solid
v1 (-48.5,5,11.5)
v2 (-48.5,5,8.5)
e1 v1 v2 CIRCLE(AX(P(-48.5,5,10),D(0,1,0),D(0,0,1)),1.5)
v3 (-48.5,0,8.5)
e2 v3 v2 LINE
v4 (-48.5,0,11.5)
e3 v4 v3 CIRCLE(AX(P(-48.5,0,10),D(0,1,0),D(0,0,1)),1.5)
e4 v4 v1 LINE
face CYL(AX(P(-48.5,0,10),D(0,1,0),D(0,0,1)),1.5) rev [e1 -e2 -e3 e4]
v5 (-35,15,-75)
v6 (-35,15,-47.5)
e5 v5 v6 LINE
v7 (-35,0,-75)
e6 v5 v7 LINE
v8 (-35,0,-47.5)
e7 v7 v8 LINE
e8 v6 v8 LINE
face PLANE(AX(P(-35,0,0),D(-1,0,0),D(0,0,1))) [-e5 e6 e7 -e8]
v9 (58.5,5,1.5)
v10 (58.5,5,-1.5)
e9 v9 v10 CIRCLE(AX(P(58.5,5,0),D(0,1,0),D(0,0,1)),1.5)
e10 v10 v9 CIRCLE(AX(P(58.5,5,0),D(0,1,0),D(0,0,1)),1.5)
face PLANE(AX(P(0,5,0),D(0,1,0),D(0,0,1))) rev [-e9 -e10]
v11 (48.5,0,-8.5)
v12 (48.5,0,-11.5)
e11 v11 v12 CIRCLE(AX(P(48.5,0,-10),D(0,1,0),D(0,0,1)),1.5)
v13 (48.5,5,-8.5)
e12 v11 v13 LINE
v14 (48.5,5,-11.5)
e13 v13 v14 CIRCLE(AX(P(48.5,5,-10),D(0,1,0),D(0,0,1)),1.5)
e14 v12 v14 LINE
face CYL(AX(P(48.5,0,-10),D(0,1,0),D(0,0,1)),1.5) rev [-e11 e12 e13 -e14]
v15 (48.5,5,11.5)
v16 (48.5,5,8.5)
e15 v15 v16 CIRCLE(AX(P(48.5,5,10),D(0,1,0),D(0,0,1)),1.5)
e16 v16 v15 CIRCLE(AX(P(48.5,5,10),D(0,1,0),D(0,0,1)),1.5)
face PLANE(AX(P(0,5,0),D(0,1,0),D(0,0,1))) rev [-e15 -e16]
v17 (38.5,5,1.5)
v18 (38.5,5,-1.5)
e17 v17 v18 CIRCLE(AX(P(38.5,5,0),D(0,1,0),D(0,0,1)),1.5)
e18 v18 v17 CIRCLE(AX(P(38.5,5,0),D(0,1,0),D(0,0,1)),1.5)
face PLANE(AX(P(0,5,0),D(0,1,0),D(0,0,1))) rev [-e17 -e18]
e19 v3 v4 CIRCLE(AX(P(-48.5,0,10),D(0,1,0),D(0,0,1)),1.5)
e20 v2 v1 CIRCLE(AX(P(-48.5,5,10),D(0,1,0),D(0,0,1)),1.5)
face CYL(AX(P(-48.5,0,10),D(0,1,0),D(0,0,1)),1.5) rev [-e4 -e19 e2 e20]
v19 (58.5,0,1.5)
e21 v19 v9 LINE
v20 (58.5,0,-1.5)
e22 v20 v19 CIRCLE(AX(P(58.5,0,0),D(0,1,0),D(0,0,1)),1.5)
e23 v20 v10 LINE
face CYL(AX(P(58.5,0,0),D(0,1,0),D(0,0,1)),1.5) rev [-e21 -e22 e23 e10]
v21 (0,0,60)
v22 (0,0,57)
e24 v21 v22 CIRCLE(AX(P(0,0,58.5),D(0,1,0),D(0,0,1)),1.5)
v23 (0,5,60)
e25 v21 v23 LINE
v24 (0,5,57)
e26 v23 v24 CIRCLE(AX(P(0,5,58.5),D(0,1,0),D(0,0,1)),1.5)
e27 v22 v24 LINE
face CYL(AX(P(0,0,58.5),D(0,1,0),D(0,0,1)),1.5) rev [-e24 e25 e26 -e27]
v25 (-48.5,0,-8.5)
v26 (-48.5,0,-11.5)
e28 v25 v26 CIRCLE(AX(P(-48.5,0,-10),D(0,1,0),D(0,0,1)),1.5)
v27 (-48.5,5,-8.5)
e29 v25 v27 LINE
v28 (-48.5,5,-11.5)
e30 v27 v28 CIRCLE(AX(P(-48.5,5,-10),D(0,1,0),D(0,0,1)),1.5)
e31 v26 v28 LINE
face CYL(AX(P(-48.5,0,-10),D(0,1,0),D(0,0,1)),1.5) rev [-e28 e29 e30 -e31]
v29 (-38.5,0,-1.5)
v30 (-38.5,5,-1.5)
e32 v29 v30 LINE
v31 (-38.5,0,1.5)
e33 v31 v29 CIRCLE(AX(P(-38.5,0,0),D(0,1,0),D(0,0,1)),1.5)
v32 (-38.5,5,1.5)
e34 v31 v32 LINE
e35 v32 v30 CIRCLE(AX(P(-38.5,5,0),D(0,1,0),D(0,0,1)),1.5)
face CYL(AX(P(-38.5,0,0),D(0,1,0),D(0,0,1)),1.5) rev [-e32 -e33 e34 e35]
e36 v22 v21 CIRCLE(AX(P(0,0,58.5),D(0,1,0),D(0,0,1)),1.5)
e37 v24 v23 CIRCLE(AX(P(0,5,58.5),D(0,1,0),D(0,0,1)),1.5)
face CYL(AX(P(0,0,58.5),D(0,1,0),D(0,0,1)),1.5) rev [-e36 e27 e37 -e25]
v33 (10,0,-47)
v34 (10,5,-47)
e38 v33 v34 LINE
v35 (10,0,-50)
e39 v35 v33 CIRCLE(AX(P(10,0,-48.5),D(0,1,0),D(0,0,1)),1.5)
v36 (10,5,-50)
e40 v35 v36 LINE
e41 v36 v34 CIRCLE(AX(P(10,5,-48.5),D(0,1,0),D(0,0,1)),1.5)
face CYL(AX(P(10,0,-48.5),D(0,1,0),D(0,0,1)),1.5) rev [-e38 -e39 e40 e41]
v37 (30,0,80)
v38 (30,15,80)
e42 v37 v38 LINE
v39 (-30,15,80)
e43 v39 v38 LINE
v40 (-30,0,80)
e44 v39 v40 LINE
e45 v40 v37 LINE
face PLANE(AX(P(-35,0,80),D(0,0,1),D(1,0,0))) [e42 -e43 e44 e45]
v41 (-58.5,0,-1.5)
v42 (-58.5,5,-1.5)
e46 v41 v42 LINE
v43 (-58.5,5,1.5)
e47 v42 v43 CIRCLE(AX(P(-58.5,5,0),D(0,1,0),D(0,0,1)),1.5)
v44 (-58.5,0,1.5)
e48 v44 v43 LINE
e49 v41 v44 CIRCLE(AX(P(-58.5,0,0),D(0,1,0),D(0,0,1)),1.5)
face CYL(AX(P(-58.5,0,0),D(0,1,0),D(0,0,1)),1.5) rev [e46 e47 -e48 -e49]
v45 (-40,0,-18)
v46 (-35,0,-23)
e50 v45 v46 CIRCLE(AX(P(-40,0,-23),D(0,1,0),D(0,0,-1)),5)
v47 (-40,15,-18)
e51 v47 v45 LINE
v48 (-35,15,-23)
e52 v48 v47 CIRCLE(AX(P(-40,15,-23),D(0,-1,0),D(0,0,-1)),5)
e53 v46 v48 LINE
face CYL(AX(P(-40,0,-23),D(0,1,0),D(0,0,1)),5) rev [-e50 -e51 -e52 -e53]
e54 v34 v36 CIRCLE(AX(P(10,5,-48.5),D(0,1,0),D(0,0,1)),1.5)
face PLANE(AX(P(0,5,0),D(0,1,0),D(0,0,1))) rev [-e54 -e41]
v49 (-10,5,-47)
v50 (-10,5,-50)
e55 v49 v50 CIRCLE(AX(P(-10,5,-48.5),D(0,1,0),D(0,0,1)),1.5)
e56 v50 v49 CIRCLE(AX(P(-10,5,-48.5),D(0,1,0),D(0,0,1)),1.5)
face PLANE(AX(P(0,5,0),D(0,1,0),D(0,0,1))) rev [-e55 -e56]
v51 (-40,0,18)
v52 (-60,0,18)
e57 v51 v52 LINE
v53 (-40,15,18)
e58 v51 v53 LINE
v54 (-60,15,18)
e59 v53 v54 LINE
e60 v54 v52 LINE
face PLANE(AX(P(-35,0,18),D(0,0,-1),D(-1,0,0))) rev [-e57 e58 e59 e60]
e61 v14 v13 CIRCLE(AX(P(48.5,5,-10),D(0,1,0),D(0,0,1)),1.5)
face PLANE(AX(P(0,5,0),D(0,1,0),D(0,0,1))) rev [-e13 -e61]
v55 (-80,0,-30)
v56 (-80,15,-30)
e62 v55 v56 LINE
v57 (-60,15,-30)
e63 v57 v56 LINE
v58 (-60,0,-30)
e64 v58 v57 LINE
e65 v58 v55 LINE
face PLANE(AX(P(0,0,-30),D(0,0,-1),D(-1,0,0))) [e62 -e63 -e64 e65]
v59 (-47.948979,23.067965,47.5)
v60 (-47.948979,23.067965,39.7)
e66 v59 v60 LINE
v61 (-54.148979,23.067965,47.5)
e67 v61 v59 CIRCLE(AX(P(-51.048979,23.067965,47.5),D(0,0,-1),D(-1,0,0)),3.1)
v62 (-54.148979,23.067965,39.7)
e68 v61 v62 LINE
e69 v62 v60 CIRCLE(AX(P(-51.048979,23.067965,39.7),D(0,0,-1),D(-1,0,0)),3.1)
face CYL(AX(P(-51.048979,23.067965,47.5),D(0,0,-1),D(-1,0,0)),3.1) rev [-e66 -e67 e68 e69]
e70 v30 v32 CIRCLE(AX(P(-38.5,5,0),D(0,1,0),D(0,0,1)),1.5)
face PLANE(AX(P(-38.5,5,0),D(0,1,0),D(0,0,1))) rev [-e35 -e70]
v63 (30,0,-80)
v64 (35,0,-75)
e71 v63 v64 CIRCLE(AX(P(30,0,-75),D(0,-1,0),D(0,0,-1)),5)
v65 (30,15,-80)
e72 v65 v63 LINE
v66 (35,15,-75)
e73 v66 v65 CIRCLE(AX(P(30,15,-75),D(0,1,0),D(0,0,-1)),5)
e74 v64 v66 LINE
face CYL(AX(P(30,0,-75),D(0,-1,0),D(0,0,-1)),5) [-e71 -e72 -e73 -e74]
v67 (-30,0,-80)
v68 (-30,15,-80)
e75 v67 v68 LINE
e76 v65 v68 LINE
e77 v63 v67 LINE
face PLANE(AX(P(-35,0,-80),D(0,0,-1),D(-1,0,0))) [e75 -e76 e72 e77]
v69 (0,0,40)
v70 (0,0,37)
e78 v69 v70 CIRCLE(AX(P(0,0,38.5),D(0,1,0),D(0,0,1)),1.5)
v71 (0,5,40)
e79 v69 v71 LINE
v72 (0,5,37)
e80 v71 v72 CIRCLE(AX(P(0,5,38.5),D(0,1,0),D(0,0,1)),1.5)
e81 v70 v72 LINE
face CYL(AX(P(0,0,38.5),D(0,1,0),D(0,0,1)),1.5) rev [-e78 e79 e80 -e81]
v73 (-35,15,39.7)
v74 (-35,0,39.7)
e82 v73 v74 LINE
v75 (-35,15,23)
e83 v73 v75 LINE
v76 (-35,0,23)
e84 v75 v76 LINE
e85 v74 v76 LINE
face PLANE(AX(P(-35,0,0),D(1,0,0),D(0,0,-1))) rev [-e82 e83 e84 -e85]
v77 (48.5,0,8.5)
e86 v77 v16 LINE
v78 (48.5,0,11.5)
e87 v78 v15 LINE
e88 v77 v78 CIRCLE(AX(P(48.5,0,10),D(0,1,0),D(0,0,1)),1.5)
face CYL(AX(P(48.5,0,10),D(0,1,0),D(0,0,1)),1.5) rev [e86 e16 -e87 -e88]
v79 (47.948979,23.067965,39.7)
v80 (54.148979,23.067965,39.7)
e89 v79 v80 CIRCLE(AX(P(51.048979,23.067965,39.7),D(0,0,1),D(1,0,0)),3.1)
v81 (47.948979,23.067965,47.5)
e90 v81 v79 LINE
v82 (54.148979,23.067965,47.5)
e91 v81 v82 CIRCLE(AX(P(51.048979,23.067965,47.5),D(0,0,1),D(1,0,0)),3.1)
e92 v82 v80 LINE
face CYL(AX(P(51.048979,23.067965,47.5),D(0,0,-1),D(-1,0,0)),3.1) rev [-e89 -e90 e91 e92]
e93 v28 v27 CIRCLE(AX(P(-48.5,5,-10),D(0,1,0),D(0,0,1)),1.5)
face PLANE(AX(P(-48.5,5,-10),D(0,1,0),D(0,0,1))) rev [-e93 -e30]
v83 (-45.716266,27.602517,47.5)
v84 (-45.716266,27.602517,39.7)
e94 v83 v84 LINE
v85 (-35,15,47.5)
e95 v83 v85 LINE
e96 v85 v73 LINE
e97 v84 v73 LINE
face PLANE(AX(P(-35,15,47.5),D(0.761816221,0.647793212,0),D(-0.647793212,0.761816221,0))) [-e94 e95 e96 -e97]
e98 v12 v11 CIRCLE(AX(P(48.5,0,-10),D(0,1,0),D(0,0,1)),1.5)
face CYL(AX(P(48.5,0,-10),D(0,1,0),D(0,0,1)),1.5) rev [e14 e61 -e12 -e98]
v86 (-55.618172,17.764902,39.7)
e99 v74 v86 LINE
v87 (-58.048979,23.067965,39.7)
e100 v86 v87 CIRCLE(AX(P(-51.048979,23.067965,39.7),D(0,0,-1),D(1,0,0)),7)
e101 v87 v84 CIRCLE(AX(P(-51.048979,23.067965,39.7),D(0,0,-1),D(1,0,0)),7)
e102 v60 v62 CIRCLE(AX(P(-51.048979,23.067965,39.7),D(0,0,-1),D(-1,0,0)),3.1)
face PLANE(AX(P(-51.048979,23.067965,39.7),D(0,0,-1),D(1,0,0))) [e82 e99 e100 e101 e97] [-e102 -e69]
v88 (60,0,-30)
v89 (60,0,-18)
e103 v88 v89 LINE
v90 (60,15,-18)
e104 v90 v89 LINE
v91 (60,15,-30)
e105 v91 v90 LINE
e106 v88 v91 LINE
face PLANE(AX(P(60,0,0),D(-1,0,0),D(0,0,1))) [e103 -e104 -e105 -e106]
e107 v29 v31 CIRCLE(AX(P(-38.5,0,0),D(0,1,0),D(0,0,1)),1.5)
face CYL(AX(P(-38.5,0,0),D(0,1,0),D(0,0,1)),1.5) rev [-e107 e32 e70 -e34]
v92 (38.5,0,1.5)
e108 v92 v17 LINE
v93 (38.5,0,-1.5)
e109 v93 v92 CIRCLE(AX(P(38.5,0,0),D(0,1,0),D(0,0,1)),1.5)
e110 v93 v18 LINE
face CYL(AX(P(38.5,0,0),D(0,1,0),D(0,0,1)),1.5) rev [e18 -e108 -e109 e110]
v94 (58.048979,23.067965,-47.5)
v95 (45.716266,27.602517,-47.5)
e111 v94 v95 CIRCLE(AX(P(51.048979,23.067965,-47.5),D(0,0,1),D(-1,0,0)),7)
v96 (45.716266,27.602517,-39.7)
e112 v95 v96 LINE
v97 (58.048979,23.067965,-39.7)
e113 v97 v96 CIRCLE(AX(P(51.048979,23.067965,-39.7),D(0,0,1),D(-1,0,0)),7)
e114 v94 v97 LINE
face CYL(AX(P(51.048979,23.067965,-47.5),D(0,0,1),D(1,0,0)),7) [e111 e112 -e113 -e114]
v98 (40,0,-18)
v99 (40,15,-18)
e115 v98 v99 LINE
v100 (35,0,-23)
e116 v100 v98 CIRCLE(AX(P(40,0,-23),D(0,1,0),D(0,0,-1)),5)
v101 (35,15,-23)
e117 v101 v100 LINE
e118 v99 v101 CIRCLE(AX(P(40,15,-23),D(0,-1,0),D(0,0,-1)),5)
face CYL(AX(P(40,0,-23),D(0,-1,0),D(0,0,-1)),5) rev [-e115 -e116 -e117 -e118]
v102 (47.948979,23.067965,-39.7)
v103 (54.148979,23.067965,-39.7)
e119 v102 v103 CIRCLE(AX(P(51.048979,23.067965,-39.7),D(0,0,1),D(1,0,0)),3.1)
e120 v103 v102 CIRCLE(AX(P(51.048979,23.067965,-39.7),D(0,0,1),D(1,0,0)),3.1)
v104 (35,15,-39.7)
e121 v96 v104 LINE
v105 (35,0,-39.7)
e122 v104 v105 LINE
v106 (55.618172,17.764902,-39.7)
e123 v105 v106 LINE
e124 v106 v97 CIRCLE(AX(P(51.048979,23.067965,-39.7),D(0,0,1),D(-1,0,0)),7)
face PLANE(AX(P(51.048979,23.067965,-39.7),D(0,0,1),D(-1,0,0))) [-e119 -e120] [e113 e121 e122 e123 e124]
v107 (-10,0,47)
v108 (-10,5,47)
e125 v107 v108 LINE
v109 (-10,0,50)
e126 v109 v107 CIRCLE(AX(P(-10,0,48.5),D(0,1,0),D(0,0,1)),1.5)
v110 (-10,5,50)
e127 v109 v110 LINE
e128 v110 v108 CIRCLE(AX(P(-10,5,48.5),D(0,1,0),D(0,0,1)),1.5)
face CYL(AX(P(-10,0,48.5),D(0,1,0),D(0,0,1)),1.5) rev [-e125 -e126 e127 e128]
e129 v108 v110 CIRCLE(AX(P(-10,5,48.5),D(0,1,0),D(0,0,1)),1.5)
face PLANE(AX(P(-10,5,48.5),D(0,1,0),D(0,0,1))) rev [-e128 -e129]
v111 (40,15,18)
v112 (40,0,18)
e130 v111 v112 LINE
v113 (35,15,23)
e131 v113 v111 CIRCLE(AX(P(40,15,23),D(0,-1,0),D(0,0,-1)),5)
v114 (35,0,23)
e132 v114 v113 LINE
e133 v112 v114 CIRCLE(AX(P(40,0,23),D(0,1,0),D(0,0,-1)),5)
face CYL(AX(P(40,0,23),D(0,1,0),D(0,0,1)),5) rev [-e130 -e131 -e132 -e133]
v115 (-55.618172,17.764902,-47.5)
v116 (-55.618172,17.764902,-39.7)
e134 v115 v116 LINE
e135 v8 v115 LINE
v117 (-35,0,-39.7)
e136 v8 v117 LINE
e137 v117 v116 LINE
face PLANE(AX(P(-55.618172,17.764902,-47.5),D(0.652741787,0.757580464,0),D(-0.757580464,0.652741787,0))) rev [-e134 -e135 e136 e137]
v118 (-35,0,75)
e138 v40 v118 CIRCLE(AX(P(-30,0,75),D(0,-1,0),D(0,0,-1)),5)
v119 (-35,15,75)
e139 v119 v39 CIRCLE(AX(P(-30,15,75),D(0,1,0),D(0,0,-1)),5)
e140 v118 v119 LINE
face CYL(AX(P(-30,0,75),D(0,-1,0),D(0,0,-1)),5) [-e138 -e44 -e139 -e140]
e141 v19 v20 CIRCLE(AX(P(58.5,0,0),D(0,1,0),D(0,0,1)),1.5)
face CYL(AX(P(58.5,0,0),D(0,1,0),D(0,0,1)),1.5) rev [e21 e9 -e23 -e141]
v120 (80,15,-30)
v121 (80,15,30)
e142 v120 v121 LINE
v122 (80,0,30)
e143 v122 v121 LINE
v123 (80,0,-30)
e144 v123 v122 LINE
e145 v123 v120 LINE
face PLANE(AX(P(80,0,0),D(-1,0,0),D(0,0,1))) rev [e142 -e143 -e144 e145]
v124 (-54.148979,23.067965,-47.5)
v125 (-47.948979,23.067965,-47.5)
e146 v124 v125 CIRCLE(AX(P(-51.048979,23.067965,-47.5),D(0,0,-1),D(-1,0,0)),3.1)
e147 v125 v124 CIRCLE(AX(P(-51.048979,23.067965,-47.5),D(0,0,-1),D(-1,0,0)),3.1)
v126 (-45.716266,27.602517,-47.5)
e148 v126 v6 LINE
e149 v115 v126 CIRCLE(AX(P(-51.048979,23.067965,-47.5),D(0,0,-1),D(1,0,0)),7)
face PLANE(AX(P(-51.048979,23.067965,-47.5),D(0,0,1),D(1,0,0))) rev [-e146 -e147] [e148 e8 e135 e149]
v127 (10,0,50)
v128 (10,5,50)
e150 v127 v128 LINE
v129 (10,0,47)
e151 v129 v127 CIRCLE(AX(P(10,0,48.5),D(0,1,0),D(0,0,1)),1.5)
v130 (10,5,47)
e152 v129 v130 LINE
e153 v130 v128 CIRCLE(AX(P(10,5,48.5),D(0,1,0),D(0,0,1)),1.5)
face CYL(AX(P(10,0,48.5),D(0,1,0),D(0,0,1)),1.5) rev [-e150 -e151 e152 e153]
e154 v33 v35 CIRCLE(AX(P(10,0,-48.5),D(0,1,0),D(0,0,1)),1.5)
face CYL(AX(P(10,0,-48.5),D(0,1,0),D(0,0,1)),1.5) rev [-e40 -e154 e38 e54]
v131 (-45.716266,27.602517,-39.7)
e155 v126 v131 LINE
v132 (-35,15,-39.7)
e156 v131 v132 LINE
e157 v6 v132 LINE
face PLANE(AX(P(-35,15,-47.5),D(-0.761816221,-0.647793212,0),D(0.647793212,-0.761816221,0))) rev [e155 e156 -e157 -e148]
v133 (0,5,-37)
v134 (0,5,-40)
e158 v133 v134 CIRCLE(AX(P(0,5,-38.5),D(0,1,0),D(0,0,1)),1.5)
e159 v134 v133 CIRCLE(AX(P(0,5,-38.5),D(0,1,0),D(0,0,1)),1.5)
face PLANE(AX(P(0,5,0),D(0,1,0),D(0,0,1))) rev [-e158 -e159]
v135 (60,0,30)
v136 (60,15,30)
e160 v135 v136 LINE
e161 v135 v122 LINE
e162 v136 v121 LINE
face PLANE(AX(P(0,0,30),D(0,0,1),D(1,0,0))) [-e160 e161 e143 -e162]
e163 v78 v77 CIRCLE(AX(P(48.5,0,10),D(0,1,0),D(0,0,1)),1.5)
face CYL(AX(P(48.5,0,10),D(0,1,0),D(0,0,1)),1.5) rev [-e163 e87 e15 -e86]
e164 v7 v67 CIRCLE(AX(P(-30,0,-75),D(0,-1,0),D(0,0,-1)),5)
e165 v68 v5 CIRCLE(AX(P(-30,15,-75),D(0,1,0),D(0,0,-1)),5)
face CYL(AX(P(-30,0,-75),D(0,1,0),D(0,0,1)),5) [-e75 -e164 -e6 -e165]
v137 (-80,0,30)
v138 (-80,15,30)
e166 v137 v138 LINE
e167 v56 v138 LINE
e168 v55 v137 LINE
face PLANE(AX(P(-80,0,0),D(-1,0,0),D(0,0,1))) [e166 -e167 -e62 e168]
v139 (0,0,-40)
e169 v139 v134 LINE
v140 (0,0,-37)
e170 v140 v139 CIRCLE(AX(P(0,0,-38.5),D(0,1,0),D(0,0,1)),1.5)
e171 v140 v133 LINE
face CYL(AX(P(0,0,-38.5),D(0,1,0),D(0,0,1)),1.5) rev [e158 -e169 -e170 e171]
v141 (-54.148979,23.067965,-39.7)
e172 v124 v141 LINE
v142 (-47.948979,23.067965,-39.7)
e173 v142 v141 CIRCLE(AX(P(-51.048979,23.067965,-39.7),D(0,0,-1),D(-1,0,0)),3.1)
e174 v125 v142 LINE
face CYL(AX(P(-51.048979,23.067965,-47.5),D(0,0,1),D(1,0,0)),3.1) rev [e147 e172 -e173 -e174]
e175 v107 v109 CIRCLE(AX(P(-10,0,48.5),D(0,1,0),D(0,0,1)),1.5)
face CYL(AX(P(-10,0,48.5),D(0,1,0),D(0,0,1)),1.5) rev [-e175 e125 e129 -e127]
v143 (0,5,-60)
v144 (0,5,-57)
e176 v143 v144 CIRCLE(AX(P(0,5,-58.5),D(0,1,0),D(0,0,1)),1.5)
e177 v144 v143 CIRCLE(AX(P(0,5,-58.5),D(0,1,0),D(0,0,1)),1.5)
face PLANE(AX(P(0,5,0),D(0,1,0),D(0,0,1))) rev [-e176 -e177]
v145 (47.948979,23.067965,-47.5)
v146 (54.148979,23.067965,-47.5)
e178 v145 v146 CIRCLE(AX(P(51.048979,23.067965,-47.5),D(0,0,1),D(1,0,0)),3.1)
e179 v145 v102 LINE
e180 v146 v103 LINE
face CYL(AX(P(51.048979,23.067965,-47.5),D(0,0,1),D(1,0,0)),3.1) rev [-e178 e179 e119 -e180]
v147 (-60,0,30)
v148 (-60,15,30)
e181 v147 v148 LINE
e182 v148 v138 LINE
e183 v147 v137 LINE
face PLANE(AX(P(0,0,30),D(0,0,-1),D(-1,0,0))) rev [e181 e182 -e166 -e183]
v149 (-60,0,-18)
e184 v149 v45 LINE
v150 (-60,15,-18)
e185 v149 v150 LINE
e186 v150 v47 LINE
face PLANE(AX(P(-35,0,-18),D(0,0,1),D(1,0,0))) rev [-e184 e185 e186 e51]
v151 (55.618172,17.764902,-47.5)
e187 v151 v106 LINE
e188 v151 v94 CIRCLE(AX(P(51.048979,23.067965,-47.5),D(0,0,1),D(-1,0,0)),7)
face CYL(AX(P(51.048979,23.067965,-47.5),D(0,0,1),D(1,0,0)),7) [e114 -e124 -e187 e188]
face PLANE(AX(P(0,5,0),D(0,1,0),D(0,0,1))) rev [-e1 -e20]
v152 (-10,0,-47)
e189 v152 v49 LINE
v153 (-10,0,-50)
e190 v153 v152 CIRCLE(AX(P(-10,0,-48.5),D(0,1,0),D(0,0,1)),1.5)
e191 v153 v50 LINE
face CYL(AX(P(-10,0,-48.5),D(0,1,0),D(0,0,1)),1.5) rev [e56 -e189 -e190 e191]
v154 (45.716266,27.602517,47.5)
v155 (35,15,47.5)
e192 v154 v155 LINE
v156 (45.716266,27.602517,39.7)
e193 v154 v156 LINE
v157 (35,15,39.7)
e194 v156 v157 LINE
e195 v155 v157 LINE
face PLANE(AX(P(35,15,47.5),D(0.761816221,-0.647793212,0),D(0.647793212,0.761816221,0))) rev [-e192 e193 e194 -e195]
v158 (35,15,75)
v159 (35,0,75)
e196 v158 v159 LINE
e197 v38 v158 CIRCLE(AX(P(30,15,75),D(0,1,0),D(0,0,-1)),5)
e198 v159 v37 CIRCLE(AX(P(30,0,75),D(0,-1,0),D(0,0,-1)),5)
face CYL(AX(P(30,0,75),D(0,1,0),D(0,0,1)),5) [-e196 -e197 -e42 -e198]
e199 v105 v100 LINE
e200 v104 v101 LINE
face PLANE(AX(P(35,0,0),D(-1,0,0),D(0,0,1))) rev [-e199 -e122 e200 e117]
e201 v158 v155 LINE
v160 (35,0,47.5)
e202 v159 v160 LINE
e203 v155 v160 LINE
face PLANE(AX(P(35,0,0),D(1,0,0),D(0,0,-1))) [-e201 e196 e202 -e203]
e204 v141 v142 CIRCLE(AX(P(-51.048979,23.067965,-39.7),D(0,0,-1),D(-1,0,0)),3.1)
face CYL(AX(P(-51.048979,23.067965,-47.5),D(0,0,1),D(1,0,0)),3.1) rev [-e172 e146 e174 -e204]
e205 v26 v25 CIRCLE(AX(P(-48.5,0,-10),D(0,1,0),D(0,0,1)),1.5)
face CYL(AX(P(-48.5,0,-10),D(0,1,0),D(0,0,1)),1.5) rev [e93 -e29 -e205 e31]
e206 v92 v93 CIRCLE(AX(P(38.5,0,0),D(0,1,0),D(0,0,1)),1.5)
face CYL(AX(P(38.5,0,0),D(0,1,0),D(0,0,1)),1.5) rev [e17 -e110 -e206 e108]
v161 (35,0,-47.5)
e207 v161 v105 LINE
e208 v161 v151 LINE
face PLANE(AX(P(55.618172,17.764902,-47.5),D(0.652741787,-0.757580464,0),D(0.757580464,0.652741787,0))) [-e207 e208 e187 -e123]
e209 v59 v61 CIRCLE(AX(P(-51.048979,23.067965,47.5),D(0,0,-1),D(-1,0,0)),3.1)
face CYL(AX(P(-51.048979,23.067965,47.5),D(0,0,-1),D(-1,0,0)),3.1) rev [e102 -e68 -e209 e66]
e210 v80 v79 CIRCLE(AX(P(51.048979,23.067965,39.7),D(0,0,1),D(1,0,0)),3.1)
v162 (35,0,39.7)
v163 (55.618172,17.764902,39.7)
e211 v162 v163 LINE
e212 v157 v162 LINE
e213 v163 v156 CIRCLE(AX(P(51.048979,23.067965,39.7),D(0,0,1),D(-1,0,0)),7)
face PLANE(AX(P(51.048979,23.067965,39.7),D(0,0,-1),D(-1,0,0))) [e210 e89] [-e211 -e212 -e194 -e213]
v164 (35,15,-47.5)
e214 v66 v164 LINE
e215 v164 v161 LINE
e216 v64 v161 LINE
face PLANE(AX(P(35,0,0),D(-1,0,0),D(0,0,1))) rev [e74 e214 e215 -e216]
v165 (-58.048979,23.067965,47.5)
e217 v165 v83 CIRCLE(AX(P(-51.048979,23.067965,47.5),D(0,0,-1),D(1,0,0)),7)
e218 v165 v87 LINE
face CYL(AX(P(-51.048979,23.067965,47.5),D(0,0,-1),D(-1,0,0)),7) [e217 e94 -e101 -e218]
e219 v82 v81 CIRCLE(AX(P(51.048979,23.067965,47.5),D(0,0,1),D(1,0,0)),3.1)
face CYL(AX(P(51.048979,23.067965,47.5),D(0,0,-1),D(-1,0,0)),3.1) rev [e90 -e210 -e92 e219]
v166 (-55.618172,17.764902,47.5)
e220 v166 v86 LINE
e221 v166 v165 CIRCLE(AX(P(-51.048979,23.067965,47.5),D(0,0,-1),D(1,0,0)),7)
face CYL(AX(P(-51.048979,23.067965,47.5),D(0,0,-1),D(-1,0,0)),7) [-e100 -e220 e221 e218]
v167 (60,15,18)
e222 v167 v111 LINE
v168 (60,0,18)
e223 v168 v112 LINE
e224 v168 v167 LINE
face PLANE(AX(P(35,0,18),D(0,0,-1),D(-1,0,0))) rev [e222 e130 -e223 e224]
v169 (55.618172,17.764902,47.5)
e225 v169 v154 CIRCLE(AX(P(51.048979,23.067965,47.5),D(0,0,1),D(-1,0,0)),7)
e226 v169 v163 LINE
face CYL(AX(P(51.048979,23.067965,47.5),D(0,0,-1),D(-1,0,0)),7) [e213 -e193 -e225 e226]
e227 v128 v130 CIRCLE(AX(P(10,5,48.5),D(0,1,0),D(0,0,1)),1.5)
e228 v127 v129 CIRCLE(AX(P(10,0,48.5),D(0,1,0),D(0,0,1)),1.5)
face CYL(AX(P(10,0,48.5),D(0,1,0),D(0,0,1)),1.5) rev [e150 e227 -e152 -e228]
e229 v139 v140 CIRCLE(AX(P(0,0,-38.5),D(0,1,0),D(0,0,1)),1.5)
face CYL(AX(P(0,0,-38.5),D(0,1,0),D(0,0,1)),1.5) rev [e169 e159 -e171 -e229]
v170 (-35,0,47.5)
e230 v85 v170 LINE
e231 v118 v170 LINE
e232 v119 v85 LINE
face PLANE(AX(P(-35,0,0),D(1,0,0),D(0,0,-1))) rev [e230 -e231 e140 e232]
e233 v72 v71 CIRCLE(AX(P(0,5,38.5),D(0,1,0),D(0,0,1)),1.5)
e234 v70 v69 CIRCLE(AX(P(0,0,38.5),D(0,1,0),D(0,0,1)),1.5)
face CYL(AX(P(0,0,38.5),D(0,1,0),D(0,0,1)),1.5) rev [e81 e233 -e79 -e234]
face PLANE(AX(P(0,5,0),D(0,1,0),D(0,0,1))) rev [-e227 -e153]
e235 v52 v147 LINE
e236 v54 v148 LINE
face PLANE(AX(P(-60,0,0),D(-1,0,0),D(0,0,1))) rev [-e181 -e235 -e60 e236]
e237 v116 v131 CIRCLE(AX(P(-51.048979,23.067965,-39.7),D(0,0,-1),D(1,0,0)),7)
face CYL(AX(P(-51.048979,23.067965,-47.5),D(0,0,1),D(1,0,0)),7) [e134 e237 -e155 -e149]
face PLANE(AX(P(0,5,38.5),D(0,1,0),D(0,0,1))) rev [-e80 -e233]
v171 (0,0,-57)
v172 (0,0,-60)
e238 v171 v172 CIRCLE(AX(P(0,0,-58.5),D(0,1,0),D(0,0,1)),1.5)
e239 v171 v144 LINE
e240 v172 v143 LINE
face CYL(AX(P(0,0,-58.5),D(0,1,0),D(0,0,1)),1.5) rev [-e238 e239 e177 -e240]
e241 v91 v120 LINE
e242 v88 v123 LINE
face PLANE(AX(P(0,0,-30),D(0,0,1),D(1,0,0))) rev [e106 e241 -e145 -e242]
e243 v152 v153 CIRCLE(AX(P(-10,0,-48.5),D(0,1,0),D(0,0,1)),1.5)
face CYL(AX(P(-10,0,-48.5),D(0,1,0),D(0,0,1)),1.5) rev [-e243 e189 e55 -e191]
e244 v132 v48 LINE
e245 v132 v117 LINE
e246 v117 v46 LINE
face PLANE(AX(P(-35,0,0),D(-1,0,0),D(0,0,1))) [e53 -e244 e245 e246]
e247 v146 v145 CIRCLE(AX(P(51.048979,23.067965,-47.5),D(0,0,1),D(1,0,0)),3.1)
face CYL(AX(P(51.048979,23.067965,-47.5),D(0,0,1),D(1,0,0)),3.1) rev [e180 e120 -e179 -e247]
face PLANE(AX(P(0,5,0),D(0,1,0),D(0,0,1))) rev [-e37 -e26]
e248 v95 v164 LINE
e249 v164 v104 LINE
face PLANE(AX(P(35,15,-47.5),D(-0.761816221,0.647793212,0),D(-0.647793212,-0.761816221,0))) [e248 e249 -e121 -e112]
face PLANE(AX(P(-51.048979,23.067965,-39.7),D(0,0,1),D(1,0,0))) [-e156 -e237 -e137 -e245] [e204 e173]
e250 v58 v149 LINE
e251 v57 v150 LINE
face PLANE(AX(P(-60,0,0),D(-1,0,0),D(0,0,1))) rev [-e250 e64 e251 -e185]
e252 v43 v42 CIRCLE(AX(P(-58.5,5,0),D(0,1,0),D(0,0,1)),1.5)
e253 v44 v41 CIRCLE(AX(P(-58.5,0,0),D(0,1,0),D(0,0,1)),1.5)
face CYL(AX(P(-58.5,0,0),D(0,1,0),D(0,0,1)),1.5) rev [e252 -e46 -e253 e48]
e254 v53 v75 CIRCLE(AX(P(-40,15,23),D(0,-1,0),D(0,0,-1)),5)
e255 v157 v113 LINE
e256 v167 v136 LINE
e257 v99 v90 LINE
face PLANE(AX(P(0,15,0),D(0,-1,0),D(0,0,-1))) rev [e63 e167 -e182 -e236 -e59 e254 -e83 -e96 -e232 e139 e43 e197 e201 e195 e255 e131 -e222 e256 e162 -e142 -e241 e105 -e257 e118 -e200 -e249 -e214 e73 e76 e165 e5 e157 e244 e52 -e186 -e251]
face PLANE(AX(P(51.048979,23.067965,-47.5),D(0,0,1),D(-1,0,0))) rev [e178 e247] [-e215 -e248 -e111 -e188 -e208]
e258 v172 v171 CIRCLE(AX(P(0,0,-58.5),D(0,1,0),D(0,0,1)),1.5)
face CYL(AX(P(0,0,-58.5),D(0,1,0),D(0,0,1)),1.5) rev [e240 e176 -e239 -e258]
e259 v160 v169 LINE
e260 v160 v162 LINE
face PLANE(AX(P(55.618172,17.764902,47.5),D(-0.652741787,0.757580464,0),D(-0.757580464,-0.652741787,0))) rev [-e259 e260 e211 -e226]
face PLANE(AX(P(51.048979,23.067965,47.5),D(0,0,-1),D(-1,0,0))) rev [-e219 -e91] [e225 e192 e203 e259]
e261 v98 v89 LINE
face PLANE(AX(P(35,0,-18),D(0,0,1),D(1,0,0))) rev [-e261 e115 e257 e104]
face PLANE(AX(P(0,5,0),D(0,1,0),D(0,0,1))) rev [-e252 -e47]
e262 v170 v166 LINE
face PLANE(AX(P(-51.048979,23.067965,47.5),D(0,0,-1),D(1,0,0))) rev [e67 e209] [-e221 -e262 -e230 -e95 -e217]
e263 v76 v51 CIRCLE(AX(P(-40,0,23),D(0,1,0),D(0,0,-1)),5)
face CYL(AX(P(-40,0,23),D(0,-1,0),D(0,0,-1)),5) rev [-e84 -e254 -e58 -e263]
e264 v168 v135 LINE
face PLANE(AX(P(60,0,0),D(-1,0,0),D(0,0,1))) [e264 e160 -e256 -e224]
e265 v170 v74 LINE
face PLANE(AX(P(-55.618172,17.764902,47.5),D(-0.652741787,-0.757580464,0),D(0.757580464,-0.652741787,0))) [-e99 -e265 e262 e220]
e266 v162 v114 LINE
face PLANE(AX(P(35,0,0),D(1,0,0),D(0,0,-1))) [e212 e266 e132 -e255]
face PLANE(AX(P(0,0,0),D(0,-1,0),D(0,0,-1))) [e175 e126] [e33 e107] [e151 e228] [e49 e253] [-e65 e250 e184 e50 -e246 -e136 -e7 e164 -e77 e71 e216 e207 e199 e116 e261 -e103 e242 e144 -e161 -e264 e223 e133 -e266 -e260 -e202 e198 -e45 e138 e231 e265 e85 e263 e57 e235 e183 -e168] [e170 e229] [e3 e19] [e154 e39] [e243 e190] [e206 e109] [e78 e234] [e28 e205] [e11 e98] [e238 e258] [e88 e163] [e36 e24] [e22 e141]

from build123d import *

# Parameters (mm, degrees)
SKETCH1_W               = 130
SKETCH1_H               = 130
BOSS_EXTRUDE1_DEPTH     = 15
SKETCH2_W               = 30
SKETCH2_H               = 30
CUT_EXTRUDE1_DEPTH      = 94.139680051
CUT_EXTRUDE4_START      = -10
SKETCH5_R               = 1.5
CUT_EXTRUDE4_DEPTH      = 84.139680051
SKETCH8_W               = 30
SKETCH8_H               = 17
CUT_EXTRUDE5_DEPTH      = 94.139680051
FILLET1_R               = 5
SKETCH9_W               = 70
SKETCH9_H               = 20
BOSS_EXTRUDE3_DEPTH     = 15
SKETCH10_R              = 3.1
BOSS_EXTRUDE4_DEPTH     = 3.9
MIRROR2_COPY_1_SKETCH_R = 3.1
MIRROR2_COPY_1_DEPTH    = 3.9
FILLET2_R               = 5
SKETCH7_W               = 20
SKETCH7_H               = 60
BOSS_EXTRUDE2_DEPTH     = 15


with BuildPart() as part:
    # Sketch1 → Boss-Extrude1 (new body)
    with BuildSketch(Plane(origin=(0, 0, 0), x_dir=(1, 0, 0), z_dir=(0, 1, 0))):
        Rectangle(SKETCH1_W, SKETCH1_H)
    extrude(amount=BOSS_EXTRUDE1_DEPTH)

    # Sketch2 → Cut-Extrude1 (cut, through all)
    with BuildSketch(Plane(origin=(0, 15, 0), x_dir=(1, 0, 0), z_dir=(0, 1, 0))):
        with Locations((-50, -50)):
            Rectangle(SKETCH2_W, SKETCH2_H)
        with Locations((-50, 50)):
            Rectangle(SKETCH2_W, SKETCH2_H)
        with Locations((50, 50)):
            Rectangle(SKETCH2_W, SKETCH2_H)
        with Locations((50, -50)):
            Rectangle(SKETCH2_W, SKETCH2_H)
    extrude(amount=-CUT_EXTRUDE1_DEPTH, mode=Mode.SUBTRACT)

    # Sketch5 → Cut-Extrude4 (cut, through all)
    with BuildSketch(Plane(origin=(0, 15, 0), x_dir=(1, 0, 0), z_dir=(0, 1, 0)).offset(CUT_EXTRUDE4_START)):
        with Locations(Location((-38.5, 0, 0), (0, 0, 270))):
            Circle(SKETCH5_R)
        with Locations(Location((-58.5, 0, 0), (0, 0, 270))):
            Circle(SKETCH5_R)
        with Locations(Location((-48.5, 10, 0), (0, 0, 270))):
            Circle(SKETCH5_R)
        with Locations(Location((-48.5, -10, 0), (0, 0, 270))):
            Circle(SKETCH5_R)
        with Locations(Location((10, 48.5, 0), (0, 0, 270))):
            Circle(SKETCH5_R)
        with Locations(Location((0, 38.5, 0), (0, 0, 270))):
            Circle(SKETCH5_R)
        with Locations(Location((-10, 48.5, 0), (0, 0, 270))):
            Circle(SKETCH5_R)
        with Locations(Location((0, 58.5, 0), (0, 0, 270))):
            Circle(SKETCH5_R)
        with Locations(Location((48.5, -10, 0), (0, 0, 270))):
            Circle(SKETCH5_R)
        with Locations(Location((38.5, 0, 0), (0, 0, 270))):
            Circle(SKETCH5_R)
        with Locations(Location((48.5, 10, 0), (0, 0, 270))):
            Circle(SKETCH5_R)
        with Locations(Location((58.5, 0, 0), (0, 0, 270))):
            Circle(SKETCH5_R)
        with Locations(Location((-10, -48.5, 0), (0, 0, 270))):
            Circle(SKETCH5_R)
        with Locations(Location((0, -38.5, 0), (0, 0, 270))):
            Circle(SKETCH5_R)
        with Locations(Location((10, -48.5, 0), (0, 0, 270))):
            Circle(SKETCH5_R)
        with Locations(Location((0, -58.5, 0), (0, 0, 270))):
            Circle(SKETCH5_R)
    extrude(amount=-CUT_EXTRUDE4_DEPTH, mode=Mode.SUBTRACT)

    # Sketch8 → Cut-Extrude5 (cut, through all)
    with BuildSketch(Plane(origin=(0, 15, 0), x_dir=(1, 0, 0), z_dir=(0, 1, 0))):
        with Locations((50, 26.5)):
            Rectangle(SKETCH8_W, SKETCH8_H)
        with Locations((50, -26.5)):
            Rectangle(SKETCH8_W, SKETCH8_H)
        with Locations((-50, 26.5)):
            Rectangle(SKETCH8_W, SKETCH8_H)
        with Locations((-50, -26.5)):
            Rectangle(SKETCH8_W, SKETCH8_H)
    extrude(amount=-CUT_EXTRUDE5_DEPTH, mode=Mode.SUBTRACT)

    # Fillet1
    fillet1_edges = [part.edges().sort_by_distance(p)[0] for p in [
        (35, 7.5, 18),
        (65, 7.5, 18),
        (-35, 7.5, -18),
        (-65, 7.5, -18),
        (-35, 7.5, 18),
        (-65, 7.5, 18),
        (35, 7.5, -18),
        (65, 7.5, -18),
        (35, 7.5, 65),
        (35, 7.5, -65),
        (-35, 7.5, -65),
        (-35, 7.5, 65),
    ]]
    fillet(fillet1_edges, radius=FILLET1_R)

    # Sketch9 → Boss-Extrude3 (add)
    with BuildSketch(Plane(origin=(0, 15, 0), x_dir=(1, 0, 0), z_dir=(0, 1, 0))):
        with Locations((0, 70)):
            Rectangle(SKETCH9_W, SKETCH9_H)
        with Locations((0, -70)):
            Rectangle(SKETCH9_W, SKETCH9_H)
    extrude(amount=-BOSS_EXTRUDE3_DEPTH)

    # Sketch10 → Boss-Extrude4 (add, symmetric)
    with BuildSketch(Plane(origin=(0, 0, -43.6), x_dir=(-1, 0, 0), z_dir=(0, 0, -1))):
        with BuildLine():
            Line((35, 15), (45.716265876, 27.602517314))
            ThreePointArc((45.716265876, 27.602517314), (55.982579723, 28.033806961), (55.61817193, 17.76490158))
            Line((55.61817193, 17.76490158), (35, 0))
            Line((35, 0), (35, 15))
        make_face()
        with Locations((51.048979422, 23.06796483)):
            Circle(SKETCH10_R, mode=Mode.SUBTRACT)
    boss_extrude4 = extrude(amount=BOSS_EXTRUDE4_DEPTH, both=True)

    # Mirror1: Boss-Extrude4 across plane
    add(boss_extrude4.mirror(Plane(origin=(0, 0, 0), x_dir=(0, 0, 1), z_dir=(1, 0, 0))))

    # Mirror2: Boss-Extrude4 across plane
    add(boss_extrude4.mirror(Plane.XY))

    # Mirror2 copy 1 sketch → Mirror2 copy 1 (add, symmetric)
    with BuildSketch(Plane.XY.offset(43.6)):
        with BuildLine():
            Line((35, 15), (45.716265876, 27.602517314))
            ThreePointArc((45.716265876, 27.602517314), (55.982579723, 28.033806961), (55.61817193, 17.76490158))
            Line((55.61817193, 17.76490158), (35, 0))
            Line((35, 0), (35, 15))
        make_face()
        with Locations((51.048979422, 23.06796483)):
            Circle(MIRROR2_COPY_1_SKETCH_R, mode=Mode.SUBTRACT)
    extrude(amount=MIRROR2_COPY_1_DEPTH, both=True)

    # Fillet2
    fillet2_edges = [part.edges().sort_by_distance(p)[0] for p in [
        (-35, 7.5, -80),
        (35, 7.5, -80),
        (-35, 7.5, 80),
        (35, 7.5, 80),
    ]]
    fillet(fillet2_edges, radius=FILLET2_R)

    # Sketch7 → Boss-Extrude2 (add)
    with BuildSketch(Plane(origin=(0, 15, 0), x_dir=(1, 0, 0), z_dir=(0, 1, 0))):
        with Locations((-70, 0)):
            Rectangle(SKETCH7_W, SKETCH7_H)
        with Locations((70, 0)):
            Rectangle(SKETCH7_W, SKETCH7_H)
    extrude(amount=-BOSS_EXTRUDE2_DEPTH)


solid = part.part
